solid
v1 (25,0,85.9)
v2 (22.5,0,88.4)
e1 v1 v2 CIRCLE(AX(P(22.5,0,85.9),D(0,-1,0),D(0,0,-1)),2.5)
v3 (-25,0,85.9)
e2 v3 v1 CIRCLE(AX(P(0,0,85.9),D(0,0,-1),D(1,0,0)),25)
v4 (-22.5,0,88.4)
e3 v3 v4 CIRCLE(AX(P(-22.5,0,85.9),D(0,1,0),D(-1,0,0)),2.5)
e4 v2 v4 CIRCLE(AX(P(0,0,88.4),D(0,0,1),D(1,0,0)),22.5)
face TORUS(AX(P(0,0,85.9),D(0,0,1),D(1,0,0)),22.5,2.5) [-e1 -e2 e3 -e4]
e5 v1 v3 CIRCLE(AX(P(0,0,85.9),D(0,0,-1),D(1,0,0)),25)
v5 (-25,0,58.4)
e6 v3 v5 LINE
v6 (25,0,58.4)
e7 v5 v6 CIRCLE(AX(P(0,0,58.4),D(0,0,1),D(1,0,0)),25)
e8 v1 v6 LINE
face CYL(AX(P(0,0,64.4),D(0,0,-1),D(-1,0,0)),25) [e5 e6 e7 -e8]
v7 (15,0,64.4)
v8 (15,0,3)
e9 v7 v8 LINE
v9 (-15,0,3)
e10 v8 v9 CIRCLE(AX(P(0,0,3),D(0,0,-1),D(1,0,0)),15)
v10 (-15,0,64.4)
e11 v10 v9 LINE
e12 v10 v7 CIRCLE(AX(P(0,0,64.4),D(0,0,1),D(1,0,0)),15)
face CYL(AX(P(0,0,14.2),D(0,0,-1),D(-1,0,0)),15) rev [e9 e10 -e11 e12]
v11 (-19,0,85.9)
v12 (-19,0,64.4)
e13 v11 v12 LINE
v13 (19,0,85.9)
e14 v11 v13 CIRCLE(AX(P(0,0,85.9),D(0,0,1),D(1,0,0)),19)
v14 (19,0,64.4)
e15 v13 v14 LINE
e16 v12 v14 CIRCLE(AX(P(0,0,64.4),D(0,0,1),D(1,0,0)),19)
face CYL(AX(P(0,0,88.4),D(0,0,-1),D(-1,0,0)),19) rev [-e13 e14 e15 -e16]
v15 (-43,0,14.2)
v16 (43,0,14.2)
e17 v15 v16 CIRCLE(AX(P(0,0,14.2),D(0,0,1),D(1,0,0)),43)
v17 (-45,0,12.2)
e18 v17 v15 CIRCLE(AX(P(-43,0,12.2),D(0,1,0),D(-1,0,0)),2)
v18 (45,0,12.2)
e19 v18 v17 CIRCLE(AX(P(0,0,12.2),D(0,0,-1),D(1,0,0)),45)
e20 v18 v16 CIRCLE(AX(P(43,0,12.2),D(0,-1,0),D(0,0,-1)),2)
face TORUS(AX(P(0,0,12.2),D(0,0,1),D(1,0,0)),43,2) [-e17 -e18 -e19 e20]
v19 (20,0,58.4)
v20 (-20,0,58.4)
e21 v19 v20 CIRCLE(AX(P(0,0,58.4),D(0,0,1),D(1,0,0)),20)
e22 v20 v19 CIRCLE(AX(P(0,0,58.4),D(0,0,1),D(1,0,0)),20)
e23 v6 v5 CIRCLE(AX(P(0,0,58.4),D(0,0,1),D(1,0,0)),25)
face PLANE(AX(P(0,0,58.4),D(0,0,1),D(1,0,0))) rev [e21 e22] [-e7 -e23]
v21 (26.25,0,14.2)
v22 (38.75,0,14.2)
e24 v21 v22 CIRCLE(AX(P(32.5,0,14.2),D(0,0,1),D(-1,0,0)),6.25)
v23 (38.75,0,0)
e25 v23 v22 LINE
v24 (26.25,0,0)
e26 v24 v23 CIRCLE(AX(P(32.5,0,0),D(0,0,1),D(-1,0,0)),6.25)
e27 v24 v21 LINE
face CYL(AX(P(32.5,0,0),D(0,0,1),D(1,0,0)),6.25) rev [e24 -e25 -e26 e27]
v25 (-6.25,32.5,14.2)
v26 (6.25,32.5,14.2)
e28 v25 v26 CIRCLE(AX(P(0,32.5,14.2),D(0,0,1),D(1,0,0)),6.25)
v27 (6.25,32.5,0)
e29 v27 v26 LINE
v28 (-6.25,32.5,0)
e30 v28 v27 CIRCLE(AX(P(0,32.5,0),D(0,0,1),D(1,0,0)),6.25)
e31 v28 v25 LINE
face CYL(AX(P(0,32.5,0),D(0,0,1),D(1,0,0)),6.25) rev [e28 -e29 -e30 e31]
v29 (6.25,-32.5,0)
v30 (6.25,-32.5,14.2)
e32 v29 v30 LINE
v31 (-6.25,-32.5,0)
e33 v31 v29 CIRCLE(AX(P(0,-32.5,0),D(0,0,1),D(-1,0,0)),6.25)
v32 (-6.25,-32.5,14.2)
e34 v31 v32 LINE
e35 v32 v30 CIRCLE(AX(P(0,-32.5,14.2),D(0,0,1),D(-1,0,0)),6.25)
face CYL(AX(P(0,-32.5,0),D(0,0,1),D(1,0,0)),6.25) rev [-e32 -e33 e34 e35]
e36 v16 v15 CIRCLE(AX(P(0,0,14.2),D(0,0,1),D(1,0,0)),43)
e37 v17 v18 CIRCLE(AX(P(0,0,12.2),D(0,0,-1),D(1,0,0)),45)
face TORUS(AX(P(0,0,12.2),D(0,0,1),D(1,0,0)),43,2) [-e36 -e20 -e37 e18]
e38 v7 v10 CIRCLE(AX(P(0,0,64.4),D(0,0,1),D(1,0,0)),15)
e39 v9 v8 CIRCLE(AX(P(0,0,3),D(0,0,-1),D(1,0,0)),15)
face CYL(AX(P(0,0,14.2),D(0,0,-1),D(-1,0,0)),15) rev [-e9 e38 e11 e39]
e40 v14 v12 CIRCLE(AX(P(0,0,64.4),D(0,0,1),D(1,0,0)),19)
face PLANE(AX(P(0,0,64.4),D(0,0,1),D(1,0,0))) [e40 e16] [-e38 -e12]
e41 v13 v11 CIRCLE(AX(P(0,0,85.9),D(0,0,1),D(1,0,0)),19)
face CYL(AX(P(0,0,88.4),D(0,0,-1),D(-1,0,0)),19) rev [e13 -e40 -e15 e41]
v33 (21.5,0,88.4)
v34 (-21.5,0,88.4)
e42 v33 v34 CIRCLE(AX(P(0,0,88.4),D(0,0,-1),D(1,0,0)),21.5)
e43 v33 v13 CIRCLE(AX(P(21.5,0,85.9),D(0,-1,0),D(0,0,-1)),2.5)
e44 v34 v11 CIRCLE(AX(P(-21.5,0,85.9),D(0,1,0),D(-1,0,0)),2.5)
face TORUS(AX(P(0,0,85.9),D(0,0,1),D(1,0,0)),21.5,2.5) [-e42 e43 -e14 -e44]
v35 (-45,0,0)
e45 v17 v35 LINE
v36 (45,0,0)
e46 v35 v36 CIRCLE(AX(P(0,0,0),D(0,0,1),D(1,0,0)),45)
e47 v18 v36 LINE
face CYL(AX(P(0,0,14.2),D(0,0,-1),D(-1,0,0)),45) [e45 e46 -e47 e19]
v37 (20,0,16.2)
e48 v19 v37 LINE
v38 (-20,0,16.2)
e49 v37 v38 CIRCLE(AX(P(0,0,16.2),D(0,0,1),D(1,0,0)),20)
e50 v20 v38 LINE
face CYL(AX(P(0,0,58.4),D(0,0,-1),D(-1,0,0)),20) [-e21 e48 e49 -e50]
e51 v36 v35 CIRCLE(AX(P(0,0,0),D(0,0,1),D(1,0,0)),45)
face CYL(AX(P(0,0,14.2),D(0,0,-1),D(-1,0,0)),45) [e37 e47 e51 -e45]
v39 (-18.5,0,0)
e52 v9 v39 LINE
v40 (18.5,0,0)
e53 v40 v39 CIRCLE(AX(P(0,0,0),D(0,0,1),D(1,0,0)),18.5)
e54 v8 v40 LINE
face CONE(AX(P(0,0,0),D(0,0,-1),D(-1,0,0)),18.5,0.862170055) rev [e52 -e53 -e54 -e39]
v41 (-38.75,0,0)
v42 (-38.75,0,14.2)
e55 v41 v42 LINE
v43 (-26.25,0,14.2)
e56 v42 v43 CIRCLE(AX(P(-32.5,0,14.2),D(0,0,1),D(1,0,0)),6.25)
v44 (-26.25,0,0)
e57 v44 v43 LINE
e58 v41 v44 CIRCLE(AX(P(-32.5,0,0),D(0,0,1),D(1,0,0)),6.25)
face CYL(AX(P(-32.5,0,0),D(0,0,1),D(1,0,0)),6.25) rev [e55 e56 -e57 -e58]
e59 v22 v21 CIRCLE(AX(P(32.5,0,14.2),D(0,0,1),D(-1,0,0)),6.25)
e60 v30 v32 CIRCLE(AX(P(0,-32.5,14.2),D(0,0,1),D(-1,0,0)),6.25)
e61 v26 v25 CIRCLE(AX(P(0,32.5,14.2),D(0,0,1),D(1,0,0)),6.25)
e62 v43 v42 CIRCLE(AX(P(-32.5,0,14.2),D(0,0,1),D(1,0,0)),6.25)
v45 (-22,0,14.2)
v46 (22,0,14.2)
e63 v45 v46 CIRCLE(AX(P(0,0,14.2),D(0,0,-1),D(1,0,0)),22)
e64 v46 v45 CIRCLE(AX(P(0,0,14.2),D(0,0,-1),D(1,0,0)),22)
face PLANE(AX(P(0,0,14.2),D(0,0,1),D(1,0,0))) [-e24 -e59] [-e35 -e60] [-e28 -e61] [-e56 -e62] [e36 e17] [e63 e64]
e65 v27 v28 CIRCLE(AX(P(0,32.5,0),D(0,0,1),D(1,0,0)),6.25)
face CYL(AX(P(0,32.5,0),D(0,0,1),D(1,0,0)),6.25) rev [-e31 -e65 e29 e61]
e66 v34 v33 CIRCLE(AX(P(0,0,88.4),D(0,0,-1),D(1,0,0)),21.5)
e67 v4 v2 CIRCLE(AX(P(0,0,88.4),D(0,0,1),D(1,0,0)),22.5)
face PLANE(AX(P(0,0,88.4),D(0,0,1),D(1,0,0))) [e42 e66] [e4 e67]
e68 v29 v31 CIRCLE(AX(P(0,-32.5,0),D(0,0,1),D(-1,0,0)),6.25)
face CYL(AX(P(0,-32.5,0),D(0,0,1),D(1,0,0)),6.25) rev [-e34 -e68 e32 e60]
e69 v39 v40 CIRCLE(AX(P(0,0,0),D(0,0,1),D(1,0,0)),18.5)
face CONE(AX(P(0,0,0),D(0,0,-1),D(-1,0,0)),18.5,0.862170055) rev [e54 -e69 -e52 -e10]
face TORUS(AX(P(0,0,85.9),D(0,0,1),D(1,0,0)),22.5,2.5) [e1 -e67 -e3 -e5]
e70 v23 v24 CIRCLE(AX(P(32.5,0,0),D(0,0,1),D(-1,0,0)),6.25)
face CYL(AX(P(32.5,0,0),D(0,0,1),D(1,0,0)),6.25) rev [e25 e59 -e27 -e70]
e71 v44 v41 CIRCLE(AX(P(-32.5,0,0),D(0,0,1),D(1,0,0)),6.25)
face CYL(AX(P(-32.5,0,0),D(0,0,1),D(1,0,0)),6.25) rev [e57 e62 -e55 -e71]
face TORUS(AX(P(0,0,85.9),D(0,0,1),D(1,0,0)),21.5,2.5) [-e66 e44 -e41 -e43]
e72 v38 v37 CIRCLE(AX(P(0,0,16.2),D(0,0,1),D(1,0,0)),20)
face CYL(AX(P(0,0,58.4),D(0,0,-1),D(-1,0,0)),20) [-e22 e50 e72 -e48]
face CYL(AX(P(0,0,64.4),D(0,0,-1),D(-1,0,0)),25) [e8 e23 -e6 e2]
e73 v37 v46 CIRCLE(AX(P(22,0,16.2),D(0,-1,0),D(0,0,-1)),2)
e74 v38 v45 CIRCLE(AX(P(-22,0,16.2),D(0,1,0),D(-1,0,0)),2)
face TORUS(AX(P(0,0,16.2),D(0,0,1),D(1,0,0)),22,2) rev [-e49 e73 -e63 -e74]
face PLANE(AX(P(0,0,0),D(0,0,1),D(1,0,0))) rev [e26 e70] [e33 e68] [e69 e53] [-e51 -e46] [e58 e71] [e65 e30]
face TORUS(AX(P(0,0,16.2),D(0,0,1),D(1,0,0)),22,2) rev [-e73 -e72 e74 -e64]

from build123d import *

# Parameters (mm, degrees)
FLANGE_PROFILE_90X_30_R     = 45
FLANGE_PROFILE_90X_30_R_2   = 15
FLANGE_90_DEPTH             = 14.2
MOUNTING_HOLES_SKETCH_R     = 6.25
FLANGE_MOUNTING_HOLES_DEPTH = 66.204601065
FLANGE_EDGE_FILLET_R2_R     = 2
HUB_PROFILE_40X_30_R        = 20
HUB_PROFILE_40X_30_R_2      = 15
HUB_40_DEPTH                = 44.2
COLLAR_PROFILE_50X_30_R     = 25
COLLAR_PROFILE_50X_30_R_2   = 15
COLLAR_50_DEPTH             = 6
SOCKET_PROFILE_50X_38_R     = 25
SOCKET_PROFILE_50X_38_R_2   = 19
SOCKET_50_DEPTH             = 24
FLANGE_CHAMFER_SIZE         = 3
FLANGE_CHAMFER_SIZE2        = 3.5
HUB_ROOT_FILLET_R2_R        = 2
SOCKET_EDGE_FILLET_R2_5_R   = 2.5


with BuildPart() as part:
    # Flange Profile Ø90xØ30 → Flange Ø90 (new body)
    with BuildSketch(Plane.XY):
        Circle(FLANGE_PROFILE_90X_30_R)
        Circle(FLANGE_PROFILE_90X_30_R_2, mode=Mode.SUBTRACT)
    extrude(amount=FLANGE_90_DEPTH)

    # Mounting Holes Sketch → Flange Mounting Holes (cut, through all)
    with BuildSketch(Plane.XY.offset(14.2)):
        with Locations((0, 32.5)):
            Circle(MOUNTING_HOLES_SKETCH_R)
        with Locations((-32.5, 0)):
            Circle(MOUNTING_HOLES_SKETCH_R)
        with Locations(Location((32.5, 0, 0), (0, 0, 180))):
            Circle(MOUNTING_HOLES_SKETCH_R)
        with Locations(Location((0, -32.5, 0), (0, 0, 180))):
            Circle(MOUNTING_HOLES_SKETCH_R)
    extrude(amount=-FLANGE_MOUNTING_HOLES_DEPTH, mode=Mode.SUBTRACT)

    # Flange Edge Fillet R2
    flange_edge_fillet_r2_edges = [part.edges().sort_by_distance(p)[0] for p in [
        (-45, 0, 14.2),
    ]]
    fillet(flange_edge_fillet_r2_edges, radius=FLANGE_EDGE_FILLET_R2_R)

    # Hub Profile Ø40xØ30 → Hub Ø40 (add)
    with BuildSketch(Plane.XY.offset(14.2)):
        Circle(HUB_PROFILE_40X_30_R)
        Circle(HUB_PROFILE_40X_30_R_2, mode=Mode.SUBTRACT)
    extrude(amount=HUB_40_DEPTH)

    # Collar Profile Ø50xØ30 → Collar Ø50 (add)
    with BuildSketch(Plane.XY.offset(58.4)):
        Circle(COLLAR_PROFILE_50X_30_R)
        Circle(COLLAR_PROFILE_50X_30_R_2, mode=Mode.SUBTRACT)
    extrude(amount=COLLAR_50_DEPTH)

    # Socket Profile Ø50xØ38 → Socket Ø50 (add)
    with BuildSketch(Plane.XY.offset(64.4)):
        Circle(SOCKET_PROFILE_50X_38_R)
        Circle(SOCKET_PROFILE_50X_38_R_2, mode=Mode.SUBTRACT)
    extrude(amount=SOCKET_50_DEPTH)

    # Flange Chamfer
    flange_chamfer_edges = [part.edges().sort_by_distance(p)[0] for p in [
        (-15, 0, 0),
    ]]
    flange_chamfer_side = [part.faces().sort_by_distance(p)[0] for p in [
        (-15, 0, 32.2),
    ]]
    chamfer(flange_chamfer_edges, length=FLANGE_CHAMFER_SIZE, length2=FLANGE_CHAMFER_SIZE2, reference=flange_chamfer_side[0])

    # Hub Root Fillet R2
    hub_root_fillet_r2_edges = [part.edges().sort_by_distance(p)[0] for p in [
        (-20, 0, 14.2),
    ]]
    fillet(hub_root_fillet_r2_edges, radius=HUB_ROOT_FILLET_R2_R)

    # Socket Edge Fillet R2.5
    socket_edge_fillet_r2_5_edges = [part.edges().sort_by_distance(p)[0] for p in [
        (-25, 0, 88.4),
        (-19, 0, 88.4),
    ]]
    fillet(socket_edge_fillet_r2_5_edges, radius=SOCKET_EDGE_FILLET_R2_5_R)


solid = part.part
